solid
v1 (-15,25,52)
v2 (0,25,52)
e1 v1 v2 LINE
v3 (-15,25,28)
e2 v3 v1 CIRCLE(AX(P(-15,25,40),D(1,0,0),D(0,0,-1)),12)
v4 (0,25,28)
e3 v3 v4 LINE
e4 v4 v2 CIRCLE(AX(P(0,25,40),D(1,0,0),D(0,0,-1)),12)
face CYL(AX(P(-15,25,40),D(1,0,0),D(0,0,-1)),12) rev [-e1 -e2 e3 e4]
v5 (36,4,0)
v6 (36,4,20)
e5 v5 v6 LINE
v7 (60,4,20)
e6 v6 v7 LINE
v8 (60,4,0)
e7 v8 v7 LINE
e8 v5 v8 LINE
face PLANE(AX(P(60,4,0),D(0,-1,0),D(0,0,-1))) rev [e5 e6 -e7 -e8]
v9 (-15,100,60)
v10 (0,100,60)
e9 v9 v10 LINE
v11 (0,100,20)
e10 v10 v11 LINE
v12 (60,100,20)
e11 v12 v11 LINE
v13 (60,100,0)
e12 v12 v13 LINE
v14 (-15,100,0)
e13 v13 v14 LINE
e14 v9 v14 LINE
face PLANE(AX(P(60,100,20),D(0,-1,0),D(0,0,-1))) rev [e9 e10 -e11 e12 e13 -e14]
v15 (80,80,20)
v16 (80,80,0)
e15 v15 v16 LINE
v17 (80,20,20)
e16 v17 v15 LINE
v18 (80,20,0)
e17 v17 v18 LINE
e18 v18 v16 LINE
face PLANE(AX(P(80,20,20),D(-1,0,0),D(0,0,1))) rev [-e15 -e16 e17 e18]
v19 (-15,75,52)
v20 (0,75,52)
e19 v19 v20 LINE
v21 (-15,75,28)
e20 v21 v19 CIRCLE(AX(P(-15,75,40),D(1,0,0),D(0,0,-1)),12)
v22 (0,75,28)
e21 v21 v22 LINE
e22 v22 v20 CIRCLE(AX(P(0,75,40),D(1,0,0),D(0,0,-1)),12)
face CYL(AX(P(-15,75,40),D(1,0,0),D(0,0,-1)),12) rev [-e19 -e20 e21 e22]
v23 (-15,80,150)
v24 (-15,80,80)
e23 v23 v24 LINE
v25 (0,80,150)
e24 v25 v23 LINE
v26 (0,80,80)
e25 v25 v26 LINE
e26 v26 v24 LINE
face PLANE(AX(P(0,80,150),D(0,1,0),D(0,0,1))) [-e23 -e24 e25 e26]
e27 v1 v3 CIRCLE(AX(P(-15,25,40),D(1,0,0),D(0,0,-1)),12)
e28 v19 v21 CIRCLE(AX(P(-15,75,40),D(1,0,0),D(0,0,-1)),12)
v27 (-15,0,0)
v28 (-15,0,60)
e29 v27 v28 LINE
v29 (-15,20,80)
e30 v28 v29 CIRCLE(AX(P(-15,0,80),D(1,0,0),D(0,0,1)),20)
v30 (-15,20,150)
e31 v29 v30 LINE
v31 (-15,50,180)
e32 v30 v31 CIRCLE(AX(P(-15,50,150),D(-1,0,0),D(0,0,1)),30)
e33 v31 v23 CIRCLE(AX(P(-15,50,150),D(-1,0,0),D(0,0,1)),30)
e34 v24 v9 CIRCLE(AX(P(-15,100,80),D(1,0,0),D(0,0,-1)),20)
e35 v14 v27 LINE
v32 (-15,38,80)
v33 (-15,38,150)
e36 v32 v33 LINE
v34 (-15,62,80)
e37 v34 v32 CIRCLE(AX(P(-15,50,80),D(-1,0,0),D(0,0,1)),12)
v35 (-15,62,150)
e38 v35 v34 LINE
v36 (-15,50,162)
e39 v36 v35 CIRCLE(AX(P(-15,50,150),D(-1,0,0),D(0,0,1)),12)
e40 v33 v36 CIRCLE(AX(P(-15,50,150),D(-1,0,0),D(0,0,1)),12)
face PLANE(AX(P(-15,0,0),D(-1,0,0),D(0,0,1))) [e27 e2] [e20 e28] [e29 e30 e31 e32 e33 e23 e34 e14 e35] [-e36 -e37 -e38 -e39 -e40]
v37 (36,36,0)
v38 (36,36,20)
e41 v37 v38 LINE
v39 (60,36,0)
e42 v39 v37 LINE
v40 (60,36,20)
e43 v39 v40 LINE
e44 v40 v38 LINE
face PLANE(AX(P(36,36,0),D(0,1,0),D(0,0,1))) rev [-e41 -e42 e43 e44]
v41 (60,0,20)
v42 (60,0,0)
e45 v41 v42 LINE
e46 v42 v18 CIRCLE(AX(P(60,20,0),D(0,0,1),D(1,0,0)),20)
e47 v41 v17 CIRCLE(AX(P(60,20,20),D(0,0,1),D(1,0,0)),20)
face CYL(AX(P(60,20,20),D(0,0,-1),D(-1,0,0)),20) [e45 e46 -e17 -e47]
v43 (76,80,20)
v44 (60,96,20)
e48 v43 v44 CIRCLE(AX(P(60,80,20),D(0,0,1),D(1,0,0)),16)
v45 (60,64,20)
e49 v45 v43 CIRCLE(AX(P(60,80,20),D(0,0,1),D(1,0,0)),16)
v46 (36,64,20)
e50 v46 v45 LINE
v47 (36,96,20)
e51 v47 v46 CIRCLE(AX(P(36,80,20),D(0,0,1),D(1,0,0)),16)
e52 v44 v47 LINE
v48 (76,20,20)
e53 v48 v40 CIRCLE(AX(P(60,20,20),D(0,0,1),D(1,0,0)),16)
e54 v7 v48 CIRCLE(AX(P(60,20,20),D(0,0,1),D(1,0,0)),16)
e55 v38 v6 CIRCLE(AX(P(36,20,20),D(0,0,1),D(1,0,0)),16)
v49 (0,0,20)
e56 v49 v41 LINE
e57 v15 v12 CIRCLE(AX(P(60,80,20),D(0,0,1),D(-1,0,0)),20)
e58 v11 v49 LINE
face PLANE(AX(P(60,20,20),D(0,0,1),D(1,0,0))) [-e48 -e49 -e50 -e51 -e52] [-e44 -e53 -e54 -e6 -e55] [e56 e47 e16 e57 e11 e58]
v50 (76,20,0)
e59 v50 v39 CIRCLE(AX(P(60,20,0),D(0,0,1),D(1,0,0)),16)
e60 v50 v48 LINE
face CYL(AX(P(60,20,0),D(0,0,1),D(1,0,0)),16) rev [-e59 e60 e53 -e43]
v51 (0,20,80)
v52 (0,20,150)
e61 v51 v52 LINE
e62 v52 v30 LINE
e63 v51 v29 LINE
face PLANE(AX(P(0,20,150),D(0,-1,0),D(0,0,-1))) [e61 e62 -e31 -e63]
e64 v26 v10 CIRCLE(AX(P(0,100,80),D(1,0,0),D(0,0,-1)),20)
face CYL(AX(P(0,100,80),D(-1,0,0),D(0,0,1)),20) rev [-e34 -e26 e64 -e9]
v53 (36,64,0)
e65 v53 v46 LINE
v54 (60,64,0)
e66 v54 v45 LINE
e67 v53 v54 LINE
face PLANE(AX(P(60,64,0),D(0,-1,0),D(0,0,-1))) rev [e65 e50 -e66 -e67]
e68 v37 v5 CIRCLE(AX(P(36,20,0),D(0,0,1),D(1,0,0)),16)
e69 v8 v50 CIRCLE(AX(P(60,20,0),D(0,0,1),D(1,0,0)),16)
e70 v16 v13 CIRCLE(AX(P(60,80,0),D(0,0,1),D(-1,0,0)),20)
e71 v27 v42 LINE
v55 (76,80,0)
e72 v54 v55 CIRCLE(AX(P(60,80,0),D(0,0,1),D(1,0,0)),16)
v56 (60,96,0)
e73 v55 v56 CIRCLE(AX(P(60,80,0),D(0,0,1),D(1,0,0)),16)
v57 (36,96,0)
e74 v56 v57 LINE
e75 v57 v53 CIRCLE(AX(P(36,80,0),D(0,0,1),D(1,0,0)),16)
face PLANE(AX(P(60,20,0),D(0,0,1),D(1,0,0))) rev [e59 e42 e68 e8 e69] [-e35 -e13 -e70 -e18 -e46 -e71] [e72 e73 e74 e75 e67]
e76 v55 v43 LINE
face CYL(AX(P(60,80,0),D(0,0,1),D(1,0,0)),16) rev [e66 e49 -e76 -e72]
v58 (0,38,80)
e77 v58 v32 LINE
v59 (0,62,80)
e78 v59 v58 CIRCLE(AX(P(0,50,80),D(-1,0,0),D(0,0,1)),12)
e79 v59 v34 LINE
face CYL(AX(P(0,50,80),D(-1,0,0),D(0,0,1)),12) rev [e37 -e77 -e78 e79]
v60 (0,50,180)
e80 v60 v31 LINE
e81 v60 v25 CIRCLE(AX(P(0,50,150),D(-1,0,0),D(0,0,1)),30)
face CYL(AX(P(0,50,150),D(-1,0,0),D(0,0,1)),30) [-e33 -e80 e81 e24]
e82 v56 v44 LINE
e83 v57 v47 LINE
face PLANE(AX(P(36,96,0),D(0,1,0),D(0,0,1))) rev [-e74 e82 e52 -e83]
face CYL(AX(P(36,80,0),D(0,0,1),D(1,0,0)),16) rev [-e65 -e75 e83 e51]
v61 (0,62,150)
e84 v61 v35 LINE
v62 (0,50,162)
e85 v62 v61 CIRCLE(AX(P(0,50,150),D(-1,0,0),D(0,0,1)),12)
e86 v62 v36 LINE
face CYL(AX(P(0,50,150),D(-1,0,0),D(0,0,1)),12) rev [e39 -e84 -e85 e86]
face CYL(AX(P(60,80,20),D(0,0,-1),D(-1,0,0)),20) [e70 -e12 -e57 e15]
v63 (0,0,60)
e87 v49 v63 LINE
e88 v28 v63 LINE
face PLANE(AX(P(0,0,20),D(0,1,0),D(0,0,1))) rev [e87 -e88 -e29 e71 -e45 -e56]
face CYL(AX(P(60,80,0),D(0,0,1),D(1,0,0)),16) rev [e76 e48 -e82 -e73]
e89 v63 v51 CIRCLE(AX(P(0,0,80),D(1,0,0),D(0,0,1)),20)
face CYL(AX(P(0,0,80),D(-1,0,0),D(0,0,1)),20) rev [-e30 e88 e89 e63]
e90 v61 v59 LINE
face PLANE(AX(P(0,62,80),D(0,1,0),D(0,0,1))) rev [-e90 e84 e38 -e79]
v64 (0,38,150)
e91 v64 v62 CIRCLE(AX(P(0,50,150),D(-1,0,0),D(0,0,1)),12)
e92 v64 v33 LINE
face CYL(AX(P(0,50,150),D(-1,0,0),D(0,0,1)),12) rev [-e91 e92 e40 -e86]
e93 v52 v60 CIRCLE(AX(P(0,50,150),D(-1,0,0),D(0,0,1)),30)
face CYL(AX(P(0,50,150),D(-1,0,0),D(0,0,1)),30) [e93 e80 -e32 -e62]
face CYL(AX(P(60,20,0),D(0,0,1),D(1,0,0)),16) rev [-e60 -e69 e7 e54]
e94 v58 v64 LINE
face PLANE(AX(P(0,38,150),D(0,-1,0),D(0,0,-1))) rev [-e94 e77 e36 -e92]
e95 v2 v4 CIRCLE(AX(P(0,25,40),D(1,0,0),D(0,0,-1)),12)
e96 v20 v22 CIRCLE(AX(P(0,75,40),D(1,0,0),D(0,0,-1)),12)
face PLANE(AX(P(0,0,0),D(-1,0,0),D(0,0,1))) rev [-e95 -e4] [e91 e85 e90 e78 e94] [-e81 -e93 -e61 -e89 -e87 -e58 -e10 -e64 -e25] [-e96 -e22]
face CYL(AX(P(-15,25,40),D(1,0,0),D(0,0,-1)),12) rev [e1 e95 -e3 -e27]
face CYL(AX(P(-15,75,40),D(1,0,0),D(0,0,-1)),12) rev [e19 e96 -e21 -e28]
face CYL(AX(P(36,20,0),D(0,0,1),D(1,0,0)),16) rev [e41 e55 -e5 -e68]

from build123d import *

# Parameters (mm, degrees)
BASE_BLOCK_DEPTH    = 20
UPRIGHT_PLATE_DEPTH = 15
SLOTTED_ARM_DEPTH   = 15
HOLES_2X_SKETCH_R   = 12
HOLES_2X_DEPTH      = 15
SLOTS_2X_DEPTH      = 20


with BuildPart() as part:
    # Base Block Sketch → Base Block (new body)
    with BuildSketch(Plane.XY):
        with BuildLine():
            Line((0, 0), (60, 0))
            ThreePointArc((60, 0), (74.142135624, 5.857864376), (80, 20))
            Line((80, 20), (80, 80))
            ThreePointArc((80, 80), (74.142135624, 94.142135624), (60, 100))
            Line((60, 100), (0, 100))
            Line((0, 100), (0, 0))
        make_face()
    extrude(amount=BASE_BLOCK_DEPTH)

    # Upright Plate Sketch → Upright Plate (add)
    with BuildSketch(Plane.ZY):
        Polygon((20, 0), (60, 0), (60, 100), (0, 100), (0, 0), align=None)
    extrude(amount=UPRIGHT_PLATE_DEPTH)

    # Slotted Arm Sketch → Slotted Arm (add)
    with BuildSketch(Plane.ZY.offset(15)):
        with BuildLine():
            Line((150, 80), (80, 80))
            ThreePointArc((80, 80), (65.857864376, 85.857864376), (60, 100))
            Line((60, 100), (60, 0))
            ThreePointArc((60, 0), (65.857864376, 14.142135624), (80, 20))
            Line((80, 20), (150, 20))
            ThreePointArc((150, 20), (180, 50), (150, 80))
        make_face()
        with BuildLine():
            Line((80, 62), (150, 62))
            ThreePointArc((150, 62), (162, 50), (150, 38))
            Line((150, 38), (80, 38))
            ThreePointArc((80, 38), (68, 50), (80, 62))
        make_face(mode=Mode.SUBTRACT)
    extrude(amount=-SLOTTED_ARM_DEPTH)

    # Holes 2x Sketch → Holes 2x (cut)
    with BuildSketch(Plane(origin=(0, 0, 0), x_dir=(0, 0, -1), z_dir=(1, 0, 0))):
        with Locations((-40, 75)):
            Circle(HOLES_2X_SKETCH_R)
        with Locations((-40, 25)):
            Circle(HOLES_2X_SKETCH_R)
    extrude(amount=-HOLES_2X_DEPTH, mode=Mode.SUBTRACT)

    # Slots 2x Sketch → Slots 2x (cut)
    with BuildSketch(Plane.XY.offset(20)):
        with BuildLine():
            Line((36, 96), (60, 96))
            ThreePointArc((60, 96), (76, 80), (60, 64))
            Line((60, 64), (36, 64))
            ThreePointArc((36, 64), (20, 80), (36, 96))
        make_face()
        with BuildLine():
            Line((36, 36), (60, 36))
            ThreePointArc((60, 36), (76, 20), (60, 4))
            Line((60, 4), (36, 4))
            ThreePointArc((36, 4), (20, 20), (36, 36))
        make_face()
    extrude(amount=-SLOTS_2X_DEPTH, mode=Mode.SUBTRACT)


solid = part.part
